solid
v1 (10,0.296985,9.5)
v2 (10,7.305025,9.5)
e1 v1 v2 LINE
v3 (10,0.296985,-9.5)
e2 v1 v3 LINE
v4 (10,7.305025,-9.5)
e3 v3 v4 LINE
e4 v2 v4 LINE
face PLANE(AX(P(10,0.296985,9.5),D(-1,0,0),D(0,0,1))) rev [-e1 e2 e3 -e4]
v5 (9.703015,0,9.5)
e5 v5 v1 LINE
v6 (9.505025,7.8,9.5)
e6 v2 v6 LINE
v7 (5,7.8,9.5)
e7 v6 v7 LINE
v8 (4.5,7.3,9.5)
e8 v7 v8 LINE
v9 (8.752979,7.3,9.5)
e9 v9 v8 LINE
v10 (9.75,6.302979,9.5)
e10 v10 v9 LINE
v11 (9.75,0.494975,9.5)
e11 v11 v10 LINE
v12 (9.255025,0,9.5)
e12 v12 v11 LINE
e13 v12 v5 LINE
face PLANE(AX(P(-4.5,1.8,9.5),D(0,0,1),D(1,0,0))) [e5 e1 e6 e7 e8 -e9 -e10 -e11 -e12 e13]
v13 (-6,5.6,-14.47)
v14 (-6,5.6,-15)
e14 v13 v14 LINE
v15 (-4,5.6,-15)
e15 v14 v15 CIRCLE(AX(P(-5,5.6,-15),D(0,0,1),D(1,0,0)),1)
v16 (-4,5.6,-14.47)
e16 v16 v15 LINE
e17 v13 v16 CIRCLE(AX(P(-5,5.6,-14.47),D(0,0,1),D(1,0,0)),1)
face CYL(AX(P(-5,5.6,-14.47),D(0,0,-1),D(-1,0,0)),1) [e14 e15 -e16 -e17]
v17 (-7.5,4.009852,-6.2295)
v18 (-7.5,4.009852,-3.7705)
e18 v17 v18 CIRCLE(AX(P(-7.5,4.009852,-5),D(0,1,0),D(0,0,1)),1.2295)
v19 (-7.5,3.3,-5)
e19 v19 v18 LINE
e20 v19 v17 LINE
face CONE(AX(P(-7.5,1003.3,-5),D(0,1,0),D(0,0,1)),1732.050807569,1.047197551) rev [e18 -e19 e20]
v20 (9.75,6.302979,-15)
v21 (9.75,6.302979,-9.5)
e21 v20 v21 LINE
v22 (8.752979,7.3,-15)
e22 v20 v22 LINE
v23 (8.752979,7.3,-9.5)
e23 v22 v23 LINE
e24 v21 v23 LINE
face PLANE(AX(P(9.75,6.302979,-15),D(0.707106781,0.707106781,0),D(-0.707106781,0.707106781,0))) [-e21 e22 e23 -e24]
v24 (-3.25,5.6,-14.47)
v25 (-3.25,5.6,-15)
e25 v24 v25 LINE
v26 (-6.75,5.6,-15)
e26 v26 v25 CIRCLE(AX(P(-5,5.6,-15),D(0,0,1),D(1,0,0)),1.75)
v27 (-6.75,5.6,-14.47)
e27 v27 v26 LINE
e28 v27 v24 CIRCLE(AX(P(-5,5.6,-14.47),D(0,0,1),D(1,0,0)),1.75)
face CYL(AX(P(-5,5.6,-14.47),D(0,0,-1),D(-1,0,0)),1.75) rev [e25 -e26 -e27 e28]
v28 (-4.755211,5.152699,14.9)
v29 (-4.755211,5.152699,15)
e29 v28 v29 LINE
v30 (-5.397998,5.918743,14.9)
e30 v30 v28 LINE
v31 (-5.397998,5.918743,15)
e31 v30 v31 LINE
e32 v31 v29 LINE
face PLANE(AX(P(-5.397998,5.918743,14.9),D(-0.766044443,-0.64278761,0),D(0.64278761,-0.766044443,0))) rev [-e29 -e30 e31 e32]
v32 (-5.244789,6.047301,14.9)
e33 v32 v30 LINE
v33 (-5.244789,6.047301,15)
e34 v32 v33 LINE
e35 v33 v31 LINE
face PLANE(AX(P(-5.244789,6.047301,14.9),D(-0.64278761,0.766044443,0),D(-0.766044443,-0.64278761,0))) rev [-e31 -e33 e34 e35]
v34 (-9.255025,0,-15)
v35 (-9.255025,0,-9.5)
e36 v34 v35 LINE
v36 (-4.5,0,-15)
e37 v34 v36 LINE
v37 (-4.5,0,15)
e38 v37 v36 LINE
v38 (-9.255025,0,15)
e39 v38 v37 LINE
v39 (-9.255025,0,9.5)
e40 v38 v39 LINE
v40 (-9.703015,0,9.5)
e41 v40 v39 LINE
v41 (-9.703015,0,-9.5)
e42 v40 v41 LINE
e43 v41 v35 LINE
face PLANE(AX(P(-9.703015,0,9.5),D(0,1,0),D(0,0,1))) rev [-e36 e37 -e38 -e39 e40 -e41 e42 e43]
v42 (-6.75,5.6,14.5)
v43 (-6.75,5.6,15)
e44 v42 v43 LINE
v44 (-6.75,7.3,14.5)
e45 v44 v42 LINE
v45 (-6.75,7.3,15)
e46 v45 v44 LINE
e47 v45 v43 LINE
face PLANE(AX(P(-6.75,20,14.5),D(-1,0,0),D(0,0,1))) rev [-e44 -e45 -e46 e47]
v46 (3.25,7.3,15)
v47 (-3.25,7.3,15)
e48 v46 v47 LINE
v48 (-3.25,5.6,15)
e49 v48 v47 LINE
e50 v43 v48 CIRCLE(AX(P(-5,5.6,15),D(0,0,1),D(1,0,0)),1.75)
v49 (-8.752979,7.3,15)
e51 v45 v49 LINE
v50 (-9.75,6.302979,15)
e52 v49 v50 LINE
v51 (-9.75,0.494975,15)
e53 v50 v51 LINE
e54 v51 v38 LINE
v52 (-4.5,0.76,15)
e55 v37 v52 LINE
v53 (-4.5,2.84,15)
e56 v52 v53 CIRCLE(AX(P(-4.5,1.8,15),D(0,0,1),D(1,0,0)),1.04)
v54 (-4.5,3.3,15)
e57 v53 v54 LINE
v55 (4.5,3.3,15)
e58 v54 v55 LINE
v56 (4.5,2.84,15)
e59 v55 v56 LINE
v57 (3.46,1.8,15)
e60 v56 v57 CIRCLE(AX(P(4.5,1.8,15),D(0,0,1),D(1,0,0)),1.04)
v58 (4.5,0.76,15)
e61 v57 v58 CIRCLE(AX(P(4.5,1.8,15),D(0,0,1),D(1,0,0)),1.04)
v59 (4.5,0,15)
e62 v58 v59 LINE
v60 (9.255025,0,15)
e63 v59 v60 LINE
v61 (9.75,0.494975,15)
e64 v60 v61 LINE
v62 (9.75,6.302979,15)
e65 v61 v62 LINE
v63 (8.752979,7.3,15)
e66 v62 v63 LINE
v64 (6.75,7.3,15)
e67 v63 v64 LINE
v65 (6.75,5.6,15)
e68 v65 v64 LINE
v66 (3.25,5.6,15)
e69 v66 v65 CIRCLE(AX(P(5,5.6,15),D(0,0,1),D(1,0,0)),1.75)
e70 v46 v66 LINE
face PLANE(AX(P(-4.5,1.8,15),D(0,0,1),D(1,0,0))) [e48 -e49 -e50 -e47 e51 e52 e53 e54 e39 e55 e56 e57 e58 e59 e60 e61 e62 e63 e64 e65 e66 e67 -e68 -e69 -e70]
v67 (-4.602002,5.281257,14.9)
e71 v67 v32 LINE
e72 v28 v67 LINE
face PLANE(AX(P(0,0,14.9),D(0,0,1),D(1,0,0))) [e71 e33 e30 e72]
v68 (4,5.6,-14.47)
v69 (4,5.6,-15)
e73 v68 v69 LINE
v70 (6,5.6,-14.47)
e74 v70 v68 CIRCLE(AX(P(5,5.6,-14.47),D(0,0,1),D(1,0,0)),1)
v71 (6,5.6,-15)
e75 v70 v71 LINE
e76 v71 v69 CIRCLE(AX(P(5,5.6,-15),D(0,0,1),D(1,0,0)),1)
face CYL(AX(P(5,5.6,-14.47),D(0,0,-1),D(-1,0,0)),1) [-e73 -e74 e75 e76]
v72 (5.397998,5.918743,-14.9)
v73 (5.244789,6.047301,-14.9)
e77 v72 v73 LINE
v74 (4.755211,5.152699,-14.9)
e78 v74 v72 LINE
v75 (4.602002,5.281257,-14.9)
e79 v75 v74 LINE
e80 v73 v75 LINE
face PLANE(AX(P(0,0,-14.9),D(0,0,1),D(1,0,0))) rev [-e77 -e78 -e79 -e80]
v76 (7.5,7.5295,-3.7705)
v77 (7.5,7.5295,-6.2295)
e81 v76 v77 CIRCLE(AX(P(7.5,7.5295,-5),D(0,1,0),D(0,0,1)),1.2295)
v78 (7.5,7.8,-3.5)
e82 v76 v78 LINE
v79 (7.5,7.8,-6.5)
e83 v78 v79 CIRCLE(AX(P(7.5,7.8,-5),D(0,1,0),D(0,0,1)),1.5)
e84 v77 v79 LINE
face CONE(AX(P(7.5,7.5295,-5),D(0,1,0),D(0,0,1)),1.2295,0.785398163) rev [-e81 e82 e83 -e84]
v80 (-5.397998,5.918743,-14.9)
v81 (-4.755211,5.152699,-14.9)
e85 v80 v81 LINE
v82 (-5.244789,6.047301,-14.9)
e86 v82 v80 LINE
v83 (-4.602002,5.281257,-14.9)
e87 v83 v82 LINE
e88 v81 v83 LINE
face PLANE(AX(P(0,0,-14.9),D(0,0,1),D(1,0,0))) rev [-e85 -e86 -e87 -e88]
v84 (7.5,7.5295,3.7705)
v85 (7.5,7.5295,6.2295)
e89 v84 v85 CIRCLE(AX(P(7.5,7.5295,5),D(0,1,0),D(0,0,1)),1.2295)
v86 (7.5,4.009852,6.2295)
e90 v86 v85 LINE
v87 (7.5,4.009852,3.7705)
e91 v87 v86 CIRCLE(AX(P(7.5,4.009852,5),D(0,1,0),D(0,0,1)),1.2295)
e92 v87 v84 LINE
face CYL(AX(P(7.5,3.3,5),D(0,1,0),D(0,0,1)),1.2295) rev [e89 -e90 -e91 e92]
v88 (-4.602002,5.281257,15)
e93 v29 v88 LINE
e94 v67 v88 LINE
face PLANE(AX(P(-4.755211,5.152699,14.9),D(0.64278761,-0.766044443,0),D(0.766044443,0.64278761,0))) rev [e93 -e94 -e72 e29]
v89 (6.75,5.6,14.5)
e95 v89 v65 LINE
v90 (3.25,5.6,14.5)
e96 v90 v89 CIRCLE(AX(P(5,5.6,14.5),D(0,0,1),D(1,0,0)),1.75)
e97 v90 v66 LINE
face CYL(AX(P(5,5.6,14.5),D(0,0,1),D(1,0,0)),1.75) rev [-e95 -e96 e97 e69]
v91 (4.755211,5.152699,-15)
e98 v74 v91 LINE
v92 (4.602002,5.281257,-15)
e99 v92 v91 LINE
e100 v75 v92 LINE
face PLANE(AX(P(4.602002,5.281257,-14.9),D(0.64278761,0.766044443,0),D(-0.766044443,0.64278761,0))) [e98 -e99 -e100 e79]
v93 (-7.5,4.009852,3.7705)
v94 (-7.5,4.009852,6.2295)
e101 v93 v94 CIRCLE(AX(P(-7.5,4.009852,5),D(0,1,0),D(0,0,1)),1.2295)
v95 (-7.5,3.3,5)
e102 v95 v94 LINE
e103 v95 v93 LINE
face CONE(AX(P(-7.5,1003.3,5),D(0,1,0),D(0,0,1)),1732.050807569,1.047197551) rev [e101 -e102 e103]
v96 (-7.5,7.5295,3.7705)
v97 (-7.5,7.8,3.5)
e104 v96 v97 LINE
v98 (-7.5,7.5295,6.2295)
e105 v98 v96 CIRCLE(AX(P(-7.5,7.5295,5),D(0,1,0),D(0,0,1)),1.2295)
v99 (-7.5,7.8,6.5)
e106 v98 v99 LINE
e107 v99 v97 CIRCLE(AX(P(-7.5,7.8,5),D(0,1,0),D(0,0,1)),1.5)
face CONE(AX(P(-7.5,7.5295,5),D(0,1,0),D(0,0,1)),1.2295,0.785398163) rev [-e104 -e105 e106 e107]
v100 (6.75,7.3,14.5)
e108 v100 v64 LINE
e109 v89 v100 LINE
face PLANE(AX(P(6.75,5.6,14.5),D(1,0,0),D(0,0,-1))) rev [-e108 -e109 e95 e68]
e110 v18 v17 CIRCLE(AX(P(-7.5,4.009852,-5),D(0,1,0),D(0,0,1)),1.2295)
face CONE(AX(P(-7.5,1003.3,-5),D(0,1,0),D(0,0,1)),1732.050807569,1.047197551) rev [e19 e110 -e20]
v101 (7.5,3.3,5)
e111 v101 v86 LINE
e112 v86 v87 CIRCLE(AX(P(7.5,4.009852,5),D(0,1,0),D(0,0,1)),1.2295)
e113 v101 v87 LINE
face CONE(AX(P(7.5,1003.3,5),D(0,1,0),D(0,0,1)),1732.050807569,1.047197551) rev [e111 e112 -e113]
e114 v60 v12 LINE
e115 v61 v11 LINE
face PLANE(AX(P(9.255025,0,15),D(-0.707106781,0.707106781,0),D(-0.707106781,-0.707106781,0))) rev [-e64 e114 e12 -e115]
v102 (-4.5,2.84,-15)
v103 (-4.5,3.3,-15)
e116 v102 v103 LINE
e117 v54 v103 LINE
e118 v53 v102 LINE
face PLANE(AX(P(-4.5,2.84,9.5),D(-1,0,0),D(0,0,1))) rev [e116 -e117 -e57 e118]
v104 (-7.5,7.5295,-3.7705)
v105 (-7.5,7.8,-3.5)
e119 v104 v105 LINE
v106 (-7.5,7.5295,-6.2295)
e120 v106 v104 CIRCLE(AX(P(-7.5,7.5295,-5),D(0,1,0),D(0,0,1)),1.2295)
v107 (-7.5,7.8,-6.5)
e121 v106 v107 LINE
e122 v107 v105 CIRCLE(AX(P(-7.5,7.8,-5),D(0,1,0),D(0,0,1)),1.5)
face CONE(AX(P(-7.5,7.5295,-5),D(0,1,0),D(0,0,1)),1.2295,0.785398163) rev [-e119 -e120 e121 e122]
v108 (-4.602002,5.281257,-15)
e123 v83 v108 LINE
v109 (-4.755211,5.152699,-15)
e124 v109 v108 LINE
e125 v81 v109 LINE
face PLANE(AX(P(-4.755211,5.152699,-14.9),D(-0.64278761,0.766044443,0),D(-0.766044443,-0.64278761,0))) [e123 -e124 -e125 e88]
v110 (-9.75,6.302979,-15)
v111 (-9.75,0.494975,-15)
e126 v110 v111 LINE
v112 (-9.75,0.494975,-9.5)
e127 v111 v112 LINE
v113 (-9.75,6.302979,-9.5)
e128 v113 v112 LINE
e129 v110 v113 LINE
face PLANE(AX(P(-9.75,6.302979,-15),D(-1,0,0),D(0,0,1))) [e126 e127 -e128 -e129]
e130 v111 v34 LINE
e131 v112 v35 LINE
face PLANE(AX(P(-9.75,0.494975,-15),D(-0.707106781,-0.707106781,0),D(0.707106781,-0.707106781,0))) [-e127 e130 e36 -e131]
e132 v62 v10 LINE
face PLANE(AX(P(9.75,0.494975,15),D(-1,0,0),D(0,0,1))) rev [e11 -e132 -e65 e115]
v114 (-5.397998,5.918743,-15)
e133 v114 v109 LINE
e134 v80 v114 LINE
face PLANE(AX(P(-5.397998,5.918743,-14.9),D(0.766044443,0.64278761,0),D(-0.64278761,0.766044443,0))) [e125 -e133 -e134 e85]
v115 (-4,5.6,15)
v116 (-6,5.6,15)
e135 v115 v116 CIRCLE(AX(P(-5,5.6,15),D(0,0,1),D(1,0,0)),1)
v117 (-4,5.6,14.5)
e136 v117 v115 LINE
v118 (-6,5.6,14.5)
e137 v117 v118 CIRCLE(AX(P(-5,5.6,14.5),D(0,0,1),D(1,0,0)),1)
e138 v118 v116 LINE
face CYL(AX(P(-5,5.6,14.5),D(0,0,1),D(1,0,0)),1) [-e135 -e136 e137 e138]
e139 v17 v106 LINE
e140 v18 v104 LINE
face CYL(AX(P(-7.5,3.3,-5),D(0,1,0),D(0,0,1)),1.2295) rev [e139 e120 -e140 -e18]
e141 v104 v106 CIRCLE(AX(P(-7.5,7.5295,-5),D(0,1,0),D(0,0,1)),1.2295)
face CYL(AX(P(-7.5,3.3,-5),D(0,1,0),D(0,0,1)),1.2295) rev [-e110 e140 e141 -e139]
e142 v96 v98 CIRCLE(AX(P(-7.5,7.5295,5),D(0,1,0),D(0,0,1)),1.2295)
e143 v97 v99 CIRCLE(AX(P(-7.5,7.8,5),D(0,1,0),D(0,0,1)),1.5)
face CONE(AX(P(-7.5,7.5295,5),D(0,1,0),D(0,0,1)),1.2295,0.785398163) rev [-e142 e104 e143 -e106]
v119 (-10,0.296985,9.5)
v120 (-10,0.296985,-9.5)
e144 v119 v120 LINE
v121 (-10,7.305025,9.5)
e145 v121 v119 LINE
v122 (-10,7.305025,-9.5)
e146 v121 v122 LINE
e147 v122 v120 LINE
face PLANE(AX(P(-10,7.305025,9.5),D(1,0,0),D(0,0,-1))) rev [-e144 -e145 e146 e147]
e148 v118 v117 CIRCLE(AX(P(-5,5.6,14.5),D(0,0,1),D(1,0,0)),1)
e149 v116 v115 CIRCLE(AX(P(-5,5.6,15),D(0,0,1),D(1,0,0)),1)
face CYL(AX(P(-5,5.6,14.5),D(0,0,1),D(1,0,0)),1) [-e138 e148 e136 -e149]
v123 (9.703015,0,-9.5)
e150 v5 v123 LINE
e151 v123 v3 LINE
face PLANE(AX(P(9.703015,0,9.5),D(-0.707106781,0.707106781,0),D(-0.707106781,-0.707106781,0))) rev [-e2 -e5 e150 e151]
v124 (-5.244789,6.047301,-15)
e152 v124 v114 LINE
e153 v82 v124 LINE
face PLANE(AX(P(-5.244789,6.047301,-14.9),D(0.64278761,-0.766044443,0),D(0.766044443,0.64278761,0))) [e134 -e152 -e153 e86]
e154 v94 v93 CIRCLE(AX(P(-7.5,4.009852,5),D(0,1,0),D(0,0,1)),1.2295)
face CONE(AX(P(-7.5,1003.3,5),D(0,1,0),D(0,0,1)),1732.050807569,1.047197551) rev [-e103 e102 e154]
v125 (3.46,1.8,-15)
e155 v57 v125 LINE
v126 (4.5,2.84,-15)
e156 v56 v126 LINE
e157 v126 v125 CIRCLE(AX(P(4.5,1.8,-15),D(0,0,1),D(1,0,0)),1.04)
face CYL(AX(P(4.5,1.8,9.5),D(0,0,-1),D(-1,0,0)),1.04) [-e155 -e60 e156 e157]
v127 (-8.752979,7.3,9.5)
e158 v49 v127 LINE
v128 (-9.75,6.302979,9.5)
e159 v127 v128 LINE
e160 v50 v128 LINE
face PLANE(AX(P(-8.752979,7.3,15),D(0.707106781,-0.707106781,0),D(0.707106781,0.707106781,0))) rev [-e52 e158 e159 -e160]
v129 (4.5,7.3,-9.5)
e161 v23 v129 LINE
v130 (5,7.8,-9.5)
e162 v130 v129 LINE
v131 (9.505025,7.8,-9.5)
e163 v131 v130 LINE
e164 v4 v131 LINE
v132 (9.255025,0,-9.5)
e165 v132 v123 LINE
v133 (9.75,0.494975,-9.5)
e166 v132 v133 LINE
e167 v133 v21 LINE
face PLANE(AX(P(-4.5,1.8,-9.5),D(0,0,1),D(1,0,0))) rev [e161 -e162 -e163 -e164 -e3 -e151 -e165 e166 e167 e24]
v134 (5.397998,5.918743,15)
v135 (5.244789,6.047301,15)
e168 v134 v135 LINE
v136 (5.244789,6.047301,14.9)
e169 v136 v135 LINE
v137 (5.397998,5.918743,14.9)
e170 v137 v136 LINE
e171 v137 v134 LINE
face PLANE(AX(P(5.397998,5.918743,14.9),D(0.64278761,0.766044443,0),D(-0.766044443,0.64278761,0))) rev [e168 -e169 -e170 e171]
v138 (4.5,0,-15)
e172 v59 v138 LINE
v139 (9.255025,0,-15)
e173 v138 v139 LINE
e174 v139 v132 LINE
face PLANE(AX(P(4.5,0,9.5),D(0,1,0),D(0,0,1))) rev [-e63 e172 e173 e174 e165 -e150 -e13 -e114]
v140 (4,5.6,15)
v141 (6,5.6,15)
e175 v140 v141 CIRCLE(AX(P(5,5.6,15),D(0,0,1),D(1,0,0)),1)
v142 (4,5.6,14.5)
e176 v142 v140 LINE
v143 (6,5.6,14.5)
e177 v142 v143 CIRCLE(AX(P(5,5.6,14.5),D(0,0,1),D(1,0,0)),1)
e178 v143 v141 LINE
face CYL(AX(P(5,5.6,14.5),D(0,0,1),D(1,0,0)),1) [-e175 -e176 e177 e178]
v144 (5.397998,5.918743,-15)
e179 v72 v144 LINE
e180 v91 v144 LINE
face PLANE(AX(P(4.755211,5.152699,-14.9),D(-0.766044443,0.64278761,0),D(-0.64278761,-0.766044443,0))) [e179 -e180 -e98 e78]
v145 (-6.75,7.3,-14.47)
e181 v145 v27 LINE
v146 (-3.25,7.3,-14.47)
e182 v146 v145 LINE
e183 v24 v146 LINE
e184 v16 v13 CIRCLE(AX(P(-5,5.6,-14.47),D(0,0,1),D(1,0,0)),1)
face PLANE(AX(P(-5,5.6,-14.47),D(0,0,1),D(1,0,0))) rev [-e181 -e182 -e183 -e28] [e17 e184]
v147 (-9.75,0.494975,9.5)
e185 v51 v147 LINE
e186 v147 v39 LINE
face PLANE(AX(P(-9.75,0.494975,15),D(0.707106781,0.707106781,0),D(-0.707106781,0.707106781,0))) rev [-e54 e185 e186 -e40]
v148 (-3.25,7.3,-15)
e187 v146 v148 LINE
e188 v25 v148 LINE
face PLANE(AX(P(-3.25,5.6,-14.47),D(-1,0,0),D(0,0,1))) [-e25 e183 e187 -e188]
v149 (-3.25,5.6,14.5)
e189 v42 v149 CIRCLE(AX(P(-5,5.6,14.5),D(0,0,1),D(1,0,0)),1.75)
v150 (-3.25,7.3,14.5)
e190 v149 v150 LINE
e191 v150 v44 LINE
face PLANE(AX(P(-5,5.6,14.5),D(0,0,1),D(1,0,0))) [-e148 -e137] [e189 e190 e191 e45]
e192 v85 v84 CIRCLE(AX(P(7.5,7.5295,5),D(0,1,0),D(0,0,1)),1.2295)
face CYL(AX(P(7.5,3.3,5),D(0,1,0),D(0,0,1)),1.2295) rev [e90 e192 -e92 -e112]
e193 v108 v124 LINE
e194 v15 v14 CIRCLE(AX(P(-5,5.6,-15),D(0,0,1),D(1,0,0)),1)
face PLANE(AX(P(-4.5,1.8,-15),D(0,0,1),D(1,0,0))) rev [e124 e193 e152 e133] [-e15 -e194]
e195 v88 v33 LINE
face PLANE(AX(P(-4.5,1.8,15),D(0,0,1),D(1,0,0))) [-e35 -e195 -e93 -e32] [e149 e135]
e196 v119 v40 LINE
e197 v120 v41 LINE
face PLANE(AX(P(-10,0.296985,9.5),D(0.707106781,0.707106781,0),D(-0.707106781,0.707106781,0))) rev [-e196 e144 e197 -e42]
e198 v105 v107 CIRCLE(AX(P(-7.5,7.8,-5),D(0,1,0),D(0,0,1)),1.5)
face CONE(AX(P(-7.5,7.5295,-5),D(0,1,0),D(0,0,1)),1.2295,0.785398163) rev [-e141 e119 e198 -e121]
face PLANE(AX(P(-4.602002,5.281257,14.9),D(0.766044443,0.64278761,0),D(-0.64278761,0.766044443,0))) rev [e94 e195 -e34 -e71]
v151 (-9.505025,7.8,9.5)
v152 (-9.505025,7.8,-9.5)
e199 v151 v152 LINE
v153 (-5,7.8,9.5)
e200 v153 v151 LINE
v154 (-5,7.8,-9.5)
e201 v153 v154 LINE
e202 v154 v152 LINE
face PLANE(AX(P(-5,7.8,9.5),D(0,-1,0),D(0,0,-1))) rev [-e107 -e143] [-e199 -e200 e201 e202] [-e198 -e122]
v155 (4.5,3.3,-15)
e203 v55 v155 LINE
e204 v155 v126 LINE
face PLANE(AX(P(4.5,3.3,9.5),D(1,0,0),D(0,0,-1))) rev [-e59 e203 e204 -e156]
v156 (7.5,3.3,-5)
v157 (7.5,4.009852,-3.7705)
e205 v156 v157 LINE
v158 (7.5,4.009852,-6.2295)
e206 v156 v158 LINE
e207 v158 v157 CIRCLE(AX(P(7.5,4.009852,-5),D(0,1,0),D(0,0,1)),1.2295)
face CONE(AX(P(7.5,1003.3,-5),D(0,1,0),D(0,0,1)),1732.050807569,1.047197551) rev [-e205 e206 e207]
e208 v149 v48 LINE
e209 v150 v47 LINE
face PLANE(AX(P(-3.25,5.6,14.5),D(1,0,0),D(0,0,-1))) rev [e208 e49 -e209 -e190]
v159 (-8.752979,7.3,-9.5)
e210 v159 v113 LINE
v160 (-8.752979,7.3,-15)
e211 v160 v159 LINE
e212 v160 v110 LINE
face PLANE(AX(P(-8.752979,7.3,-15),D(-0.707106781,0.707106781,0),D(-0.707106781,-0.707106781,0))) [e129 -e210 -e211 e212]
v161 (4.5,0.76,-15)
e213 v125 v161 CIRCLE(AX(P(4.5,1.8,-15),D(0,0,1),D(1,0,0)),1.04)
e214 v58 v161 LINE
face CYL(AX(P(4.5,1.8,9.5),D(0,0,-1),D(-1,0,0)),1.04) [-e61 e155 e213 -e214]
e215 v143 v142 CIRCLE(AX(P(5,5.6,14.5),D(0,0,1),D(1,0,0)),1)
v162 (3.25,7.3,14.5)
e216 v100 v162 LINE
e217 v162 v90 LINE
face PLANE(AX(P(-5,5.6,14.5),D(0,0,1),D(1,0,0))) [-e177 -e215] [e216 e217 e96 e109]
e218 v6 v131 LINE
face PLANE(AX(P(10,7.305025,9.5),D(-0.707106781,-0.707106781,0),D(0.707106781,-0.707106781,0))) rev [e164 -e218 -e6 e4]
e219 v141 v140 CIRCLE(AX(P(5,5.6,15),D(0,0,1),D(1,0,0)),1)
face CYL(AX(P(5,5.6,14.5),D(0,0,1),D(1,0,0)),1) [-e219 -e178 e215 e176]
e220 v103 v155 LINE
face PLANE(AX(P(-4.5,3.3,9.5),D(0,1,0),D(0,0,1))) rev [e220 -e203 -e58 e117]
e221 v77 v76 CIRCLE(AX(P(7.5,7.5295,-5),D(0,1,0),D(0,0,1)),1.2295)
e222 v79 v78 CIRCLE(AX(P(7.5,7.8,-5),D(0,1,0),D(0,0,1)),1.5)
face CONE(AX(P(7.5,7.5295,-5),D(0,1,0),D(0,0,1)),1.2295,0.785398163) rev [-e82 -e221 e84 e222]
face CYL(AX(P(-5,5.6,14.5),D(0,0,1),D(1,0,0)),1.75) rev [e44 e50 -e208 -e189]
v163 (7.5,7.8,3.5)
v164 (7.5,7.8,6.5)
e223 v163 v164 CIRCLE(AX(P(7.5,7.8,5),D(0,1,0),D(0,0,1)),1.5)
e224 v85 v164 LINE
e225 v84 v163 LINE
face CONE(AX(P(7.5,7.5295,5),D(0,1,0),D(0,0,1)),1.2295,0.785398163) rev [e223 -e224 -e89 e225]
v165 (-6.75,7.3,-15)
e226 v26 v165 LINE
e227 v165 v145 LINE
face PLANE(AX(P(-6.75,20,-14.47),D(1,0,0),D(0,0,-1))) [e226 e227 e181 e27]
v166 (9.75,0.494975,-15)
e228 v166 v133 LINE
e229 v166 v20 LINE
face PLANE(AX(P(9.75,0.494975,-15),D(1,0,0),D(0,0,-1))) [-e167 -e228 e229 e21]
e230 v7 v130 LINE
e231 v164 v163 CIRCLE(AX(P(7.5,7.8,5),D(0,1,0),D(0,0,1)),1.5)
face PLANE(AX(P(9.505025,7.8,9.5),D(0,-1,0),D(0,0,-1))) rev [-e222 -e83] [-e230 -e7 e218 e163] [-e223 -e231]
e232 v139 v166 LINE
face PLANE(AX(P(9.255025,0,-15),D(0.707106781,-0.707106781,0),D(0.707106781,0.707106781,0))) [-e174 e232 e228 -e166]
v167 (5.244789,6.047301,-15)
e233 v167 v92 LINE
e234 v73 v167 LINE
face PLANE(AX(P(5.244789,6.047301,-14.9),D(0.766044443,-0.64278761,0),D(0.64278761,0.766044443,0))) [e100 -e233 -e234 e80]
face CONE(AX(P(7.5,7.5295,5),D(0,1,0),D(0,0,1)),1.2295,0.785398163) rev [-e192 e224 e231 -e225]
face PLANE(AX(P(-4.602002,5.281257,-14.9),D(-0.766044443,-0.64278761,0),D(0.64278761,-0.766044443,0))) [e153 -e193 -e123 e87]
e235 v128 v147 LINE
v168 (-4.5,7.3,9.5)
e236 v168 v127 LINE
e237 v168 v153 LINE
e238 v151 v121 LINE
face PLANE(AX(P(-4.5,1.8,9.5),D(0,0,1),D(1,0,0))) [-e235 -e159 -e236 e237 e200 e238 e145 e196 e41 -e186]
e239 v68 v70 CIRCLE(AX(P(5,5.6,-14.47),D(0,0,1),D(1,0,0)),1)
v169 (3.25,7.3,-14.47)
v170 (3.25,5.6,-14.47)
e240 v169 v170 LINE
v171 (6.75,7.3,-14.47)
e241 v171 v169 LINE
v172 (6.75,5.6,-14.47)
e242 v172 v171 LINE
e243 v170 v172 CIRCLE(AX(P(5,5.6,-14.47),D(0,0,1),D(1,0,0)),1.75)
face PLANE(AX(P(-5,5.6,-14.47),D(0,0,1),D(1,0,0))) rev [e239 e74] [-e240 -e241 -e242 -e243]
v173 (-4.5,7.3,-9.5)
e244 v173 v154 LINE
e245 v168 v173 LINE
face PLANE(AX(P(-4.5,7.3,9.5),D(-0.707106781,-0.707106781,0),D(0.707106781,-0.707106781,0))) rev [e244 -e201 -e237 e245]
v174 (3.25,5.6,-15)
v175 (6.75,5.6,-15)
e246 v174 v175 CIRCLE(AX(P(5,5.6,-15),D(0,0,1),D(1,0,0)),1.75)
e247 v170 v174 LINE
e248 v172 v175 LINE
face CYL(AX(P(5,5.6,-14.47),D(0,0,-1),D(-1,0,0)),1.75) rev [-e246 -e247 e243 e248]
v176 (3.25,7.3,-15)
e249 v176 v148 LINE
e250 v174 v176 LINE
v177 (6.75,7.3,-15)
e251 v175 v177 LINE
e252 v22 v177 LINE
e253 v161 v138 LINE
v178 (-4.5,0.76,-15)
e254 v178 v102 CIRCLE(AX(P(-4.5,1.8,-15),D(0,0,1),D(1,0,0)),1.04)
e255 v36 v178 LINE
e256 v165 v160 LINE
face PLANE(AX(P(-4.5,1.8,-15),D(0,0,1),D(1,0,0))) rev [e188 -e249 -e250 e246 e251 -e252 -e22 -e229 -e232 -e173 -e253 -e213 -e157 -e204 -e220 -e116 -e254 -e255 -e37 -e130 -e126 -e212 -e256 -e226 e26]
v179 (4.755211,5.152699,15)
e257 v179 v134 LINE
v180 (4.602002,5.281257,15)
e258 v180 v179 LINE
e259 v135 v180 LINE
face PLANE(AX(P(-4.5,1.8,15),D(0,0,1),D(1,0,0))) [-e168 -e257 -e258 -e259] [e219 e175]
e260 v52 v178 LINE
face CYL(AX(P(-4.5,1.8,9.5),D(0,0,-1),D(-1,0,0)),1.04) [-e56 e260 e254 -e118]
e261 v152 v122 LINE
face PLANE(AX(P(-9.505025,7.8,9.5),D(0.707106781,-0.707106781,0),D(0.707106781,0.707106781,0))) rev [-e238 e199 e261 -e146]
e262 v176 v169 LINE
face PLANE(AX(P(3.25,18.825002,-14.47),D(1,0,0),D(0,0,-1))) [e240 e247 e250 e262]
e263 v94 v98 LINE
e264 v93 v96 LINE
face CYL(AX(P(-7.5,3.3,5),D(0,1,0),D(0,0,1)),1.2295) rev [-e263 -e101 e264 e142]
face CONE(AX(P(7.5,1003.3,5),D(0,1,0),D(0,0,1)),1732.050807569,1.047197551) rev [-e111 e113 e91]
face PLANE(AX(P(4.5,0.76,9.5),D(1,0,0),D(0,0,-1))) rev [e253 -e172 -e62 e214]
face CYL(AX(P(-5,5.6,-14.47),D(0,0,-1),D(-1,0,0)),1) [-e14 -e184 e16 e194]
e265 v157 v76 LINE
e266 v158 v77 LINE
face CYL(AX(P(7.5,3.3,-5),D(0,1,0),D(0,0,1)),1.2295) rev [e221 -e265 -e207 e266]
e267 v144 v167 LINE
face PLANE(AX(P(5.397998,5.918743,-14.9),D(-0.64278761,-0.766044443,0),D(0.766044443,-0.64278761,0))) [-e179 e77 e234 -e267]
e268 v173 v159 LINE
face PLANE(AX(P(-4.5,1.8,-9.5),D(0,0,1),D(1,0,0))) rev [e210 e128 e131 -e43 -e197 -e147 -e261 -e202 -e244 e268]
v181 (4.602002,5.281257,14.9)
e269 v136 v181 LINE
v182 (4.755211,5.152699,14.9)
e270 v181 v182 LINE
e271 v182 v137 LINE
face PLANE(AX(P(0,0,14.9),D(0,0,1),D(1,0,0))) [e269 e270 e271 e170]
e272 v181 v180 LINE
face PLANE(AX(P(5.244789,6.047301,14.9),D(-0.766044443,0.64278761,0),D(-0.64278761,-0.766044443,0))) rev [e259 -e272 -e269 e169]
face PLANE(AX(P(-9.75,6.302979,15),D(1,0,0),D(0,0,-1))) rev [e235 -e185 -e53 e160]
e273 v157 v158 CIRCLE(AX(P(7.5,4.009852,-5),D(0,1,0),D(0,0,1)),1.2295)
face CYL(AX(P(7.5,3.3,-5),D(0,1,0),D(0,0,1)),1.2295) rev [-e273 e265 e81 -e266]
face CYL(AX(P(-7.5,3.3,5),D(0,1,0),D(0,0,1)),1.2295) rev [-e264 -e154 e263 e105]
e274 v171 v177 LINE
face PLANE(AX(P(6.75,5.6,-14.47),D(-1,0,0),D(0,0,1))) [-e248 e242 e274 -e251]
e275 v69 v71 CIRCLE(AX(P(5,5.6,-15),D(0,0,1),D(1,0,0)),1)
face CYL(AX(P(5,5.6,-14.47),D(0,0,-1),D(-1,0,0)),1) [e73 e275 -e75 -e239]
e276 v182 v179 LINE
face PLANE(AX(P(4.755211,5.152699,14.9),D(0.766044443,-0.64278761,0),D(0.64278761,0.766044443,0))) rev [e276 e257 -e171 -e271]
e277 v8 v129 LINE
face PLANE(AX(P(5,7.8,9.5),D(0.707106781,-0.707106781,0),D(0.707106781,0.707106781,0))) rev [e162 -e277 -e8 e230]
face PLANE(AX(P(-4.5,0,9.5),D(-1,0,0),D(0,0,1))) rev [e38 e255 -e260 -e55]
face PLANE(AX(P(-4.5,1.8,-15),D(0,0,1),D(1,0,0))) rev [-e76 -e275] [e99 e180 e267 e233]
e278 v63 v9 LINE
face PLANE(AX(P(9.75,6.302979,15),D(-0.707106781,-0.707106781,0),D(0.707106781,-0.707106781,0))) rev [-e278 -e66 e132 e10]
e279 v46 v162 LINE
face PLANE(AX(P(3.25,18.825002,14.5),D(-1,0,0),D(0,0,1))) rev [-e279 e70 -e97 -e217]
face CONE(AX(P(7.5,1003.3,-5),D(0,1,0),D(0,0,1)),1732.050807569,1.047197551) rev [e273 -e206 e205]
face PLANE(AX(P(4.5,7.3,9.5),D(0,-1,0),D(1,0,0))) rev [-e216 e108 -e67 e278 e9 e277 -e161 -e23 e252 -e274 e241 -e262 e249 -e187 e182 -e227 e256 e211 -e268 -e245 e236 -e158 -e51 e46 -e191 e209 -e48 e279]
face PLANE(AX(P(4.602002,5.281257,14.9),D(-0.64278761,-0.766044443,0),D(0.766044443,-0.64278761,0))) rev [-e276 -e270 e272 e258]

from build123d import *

# Parameters (mm, degrees)
BOSS_EXTRUDE1_DEPTH      = 9.5
BOSS_EXTRUDE1_DEPTH_BACK = 9.5
BOSS_EXTRUDE2_DEPTH      = 5.5
BOSS_EXTRUDE3_START      = -5.5
BOSS_EXTRUDE3_DEPTH      = 5.5
SKETCH4_R                = 1
CUT_EXTRUDE1_DEPTH       = 0.53
CUT_EXTRUDE2_START       = -0.5
SKETCH5_R                = 1
CUT_EXTRUDE2_DEPTH       = 0.5
LPATTERN1_COUNT          = 2
LPATTERN1_PITCH          = 10
LPATTERN1_COUNT_DIR2     = 2
LPATTERN1_PITCH_DIR2     = 15
CUT_EXTRUDE3_DEPTH       = 0.1
CUT_EXTRUDE4_DEPTH       = 0.1
CUT_EXTRUDE5_DEPTH       = 0.1
CUT_EXTRUDE6_DEPTH       = 0.1


with BuildPart() as part:
    # Sketch1 → Boss-Extrude1 (new, two sides: drawn at the far end of the back side and taken through both)
    with BuildSketch(Plane.XY.offset(-BOSS_EXTRUDE1_DEPTH_BACK)):
        with BuildLine():
            Line((-10, 7.305025253), (-10, 0.296984848))
            Line((-10, 0.296984848), (-9.703015152, 0))
            Line((-9.703015152, 0), (-4.5, 0))
            Line((-4.5, 0), (-4.5, 0.76))
            ThreePointArc((-4.5, 0.76), (-3.46, 1.8), (-4.5, 2.84))
            Line((-4.5, 2.84), (-4.5, 3.3))
            Line((-4.5, 3.3), (4.5, 3.3))
            Line((4.5, 3.3), (4.5, 2.84))
            ThreePointArc((4.5, 2.84), (3.46, 1.8), (4.5, 0.76))
            Line((4.5, 0.76), (4.5, 0))
            Line((4.5, 0), (9.703015152, 0))
            Line((9.703015152, 0), (10, 0.296984848))
            Line((10, 0.296984848), (10, 7.305025253))
            Line((10, 7.305025253), (9.505025253, 7.8))
            Line((9.505025253, 7.8), (5, 7.8))
            Line((5, 7.8), (4.5, 7.3))
            Line((4.5, 7.3), (-4.5, 7.3))
            Line((-4.5, 7.3), (-5, 7.8))
            Line((-5, 7.8), (-9.505025253, 7.8))
            Line((-9.505025253, 7.8), (-10, 7.305025253))
        make_face()
    extrude(amount=BOSS_EXTRUDE1_DEPTH + BOSS_EXTRUDE1_DEPTH_BACK)

    # Sketch2 → Boss-Extrude2 (add)
    with BuildSketch(Plane.XY.offset(9.5)):
        with BuildLine():
            Line((-9.75, 6.302979439), (-9.75, 0.494974747))
            Line((-9.75, 0.494974747), (-9.255025253, 0))
            Line((-9.255025253, 0), (-4.5, 0))
            Line((-4.5, 0), (-4.5, 0.76))
            ThreePointArc((-4.5, 0.76), (-3.46, 1.8), (-4.5, 2.84))
            Line((-4.5, 2.84), (-4.5, 3.3))
            Line((-4.5, 3.3), (4.5, 3.3))
            Line((4.5, 3.3), (4.5, 2.84))
            ThreePointArc((4.5, 2.84), (3.46, 1.8), (4.5, 0.76))
            Line((4.5, 0.76), (4.5, 0))
            Line((4.5, 0), (9.255025253, 0))
            Line((9.255025253, 0), (9.75, 0.494974747))
            Line((9.75, 0.494974747), (9.75, 6.302979439))
            Line((9.75, 6.302979439), (8.752979439, 7.3))
            Line((8.752979439, 7.3), (-8.752979439, 7.3))
            Line((-8.752979439, 7.3), (-9.75, 6.302979439))
        make_face()
    extrude(amount=BOSS_EXTRUDE2_DEPTH)

    # Sketch3 → Boss-Extrude3 (add)
    with BuildSketch(Plane.XY.offset(-9.5).offset(BOSS_EXTRUDE3_START)):
        with BuildLine():
            Line((-9.75, 6.302979439), (-9.75, 0.494974747))
            Line((-9.75, 0.494974747), (-9.255025253, 0))
            Line((-9.255025253, 0), (-4.5, 0))
            Line((-4.5, 0), (-4.5, 0.76))
            ThreePointArc((-4.5, 0.76), (-3.46, 1.8), (-4.5, 2.84))
            Line((-4.5, 2.84), (-4.5, 3.3))
            Line((-4.5, 3.3), (4.5, 3.3))
            Line((4.5, 3.3), (4.5, 2.84))
            ThreePointArc((4.5, 2.84), (3.46, 1.8), (4.5, 0.76))
            Line((4.5, 0.76), (4.5, 0))
            Line((4.5, 0), (9.255025253, 0))
            Line((9.255025253, 0), (9.75, 0.494974747))
            Line((9.75, 0.494974747), (9.75, 6.302979439))
            Line((9.75, 6.302979439), (8.752979439, 7.3))
            Line((8.752979439, 7.3), (-8.752979439, 7.3))
            Line((-8.752979439, 7.3), (-9.75, 6.302979439))
        make_face()
    extrude(amount=BOSS_EXTRUDE3_DEPTH)

    # Sketch4 → Cut-Extrude1 (cut)
    with BuildSketch(Plane.XY.offset(-15)):
        with BuildLine():
            Line((-6.75, 20), (-6.75, 5.6))
            ThreePointArc((-6.75, 5.6), (-5, 3.85), (-3.25, 5.6))
            Line((-3.25, 5.6), (-3.25, 18.82500207))
            Line((-3.25, 18.82500207), (3.25, 18.82500207))
            Line((3.25, 18.82500207), (3.25, 5.6))
            ThreePointArc((3.25, 5.6), (5, 3.85), (6.75, 5.6))
            Line((6.75, 5.6), (6.75, 20))
            Line((6.75, 20), (-6.75, 20))
        make_face()
        with Locations((5, 5.6)):
            Circle(SKETCH4_R, mode=Mode.SUBTRACT)
        with Locations((-5, 5.6)):
            Circle(SKETCH4_R, mode=Mode.SUBTRACT)
    extrude(amount=CUT_EXTRUDE1_DEPTH, mode=Mode.SUBTRACT)

    # Sketch5 → Cut-Extrude2 (cut)
    with BuildSketch(Plane.XY.offset(15).offset(CUT_EXTRUDE2_START)):
        with BuildLine():
            Line((-6.75, 20), (-6.75, 5.6))
            ThreePointArc((-6.75, 5.6), (-5, 3.85), (-3.25, 5.6))
            Line((-3.25, 5.6), (-3.25, 18.82500207))
            Line((-3.25, 18.82500207), (3.25, 18.82500207))
            Line((3.25, 18.82500207), (3.25, 5.6))
            ThreePointArc((3.25, 5.6), (5, 3.85), (6.75, 5.6))
            Line((6.75, 5.6), (6.75, 20))
            Line((6.75, 20), (-6.75, 20))
        make_face()
        with Locations((5, 5.6)):
            Circle(SKETCH5_R, mode=Mode.SUBTRACT)
        with Locations((-5, 5.6)):
            Circle(SKETCH5_R, mode=Mode.SUBTRACT)
    extrude(amount=CUT_EXTRUDE2_DEPTH, mode=Mode.SUBTRACT)

    # Sketch6 → Cut-Revolve1 (revolve, cut)
    with BuildSketch(Plane(origin=(7.5, 0, 0), x_dir=(0, 0, -1), z_dir=(1, 0, 0)), mode=Mode.PRIVATE) as cut_revolve1_sk:
        Polygon((-5, 7.8), (-3.5, 7.8), (-3.7705, 7.5295), (-3.7705, 4.009852156), (-5, 3.3), align=None)
    cut_revolve1 = revolve(cut_revolve1_sk.sketch.rotate(Axis((7.5, 3.3, 5), (0, 1, 0)), 180), axis=Axis((7.5, 3.3, 5), (0, 1, 0)), mode=Mode.SUBTRACT)

    # LPattern1: Cut-Revolve1 2 × 2
    with Locations(*[(-j * LPATTERN1_PITCH_DIR2, 0, -i * LPATTERN1_PITCH) for i in range(LPATTERN1_COUNT) for j in range(LPATTERN1_COUNT_DIR2) if (i, j) != (0, 0)]):
        add(cut_revolve1, mode=Mode.SUBTRACT)

    # Sketch8 → Cut-Extrude3 (cut)
    with BuildSketch(Plane.XY.offset(15)):
        Polygon((4.602001751, 5.281256539), (4.755210639, 5.152699017), (5.397998249, 5.918743461), (5.244789361, 6.047300983), align=None)
    extrude(amount=-CUT_EXTRUDE3_DEPTH, mode=Mode.SUBTRACT)

    # Sketch9 → Cut-Extrude4 (cut)
    with BuildSketch(Plane.XY.offset(15)):
        Polygon((-5.397998249, 5.918743461), (-4.755210639, 5.152699017), (-4.602001751, 5.281256539), (-5.244789361, 6.047300983), align=None)
    extrude(amount=-CUT_EXTRUDE4_DEPTH, mode=Mode.SUBTRACT)

    # Sketch10 → Cut-Extrude5 (cut)
    with BuildSketch(Plane.XY.offset(-15)):
        Polygon((4.602001751, 5.281256539), (4.755210639, 5.152699017), (5.397998249, 5.918743461), (5.244789361, 6.047300983), align=None)
    extrude(amount=CUT_EXTRUDE5_DEPTH, mode=Mode.SUBTRACT)

    # Sketch11 → Cut-Extrude6 (cut)
    with BuildSketch(Plane.XY.offset(-15)):
        Polygon((-5.397998249, 5.918743461), (-4.755210639, 5.152699017), (-4.602001751, 5.281256539), (-5.244789361, 6.047300983), align=None)
    extrude(amount=CUT_EXTRUDE6_DEPTH, mode=Mode.SUBTRACT)


solid = part.part
